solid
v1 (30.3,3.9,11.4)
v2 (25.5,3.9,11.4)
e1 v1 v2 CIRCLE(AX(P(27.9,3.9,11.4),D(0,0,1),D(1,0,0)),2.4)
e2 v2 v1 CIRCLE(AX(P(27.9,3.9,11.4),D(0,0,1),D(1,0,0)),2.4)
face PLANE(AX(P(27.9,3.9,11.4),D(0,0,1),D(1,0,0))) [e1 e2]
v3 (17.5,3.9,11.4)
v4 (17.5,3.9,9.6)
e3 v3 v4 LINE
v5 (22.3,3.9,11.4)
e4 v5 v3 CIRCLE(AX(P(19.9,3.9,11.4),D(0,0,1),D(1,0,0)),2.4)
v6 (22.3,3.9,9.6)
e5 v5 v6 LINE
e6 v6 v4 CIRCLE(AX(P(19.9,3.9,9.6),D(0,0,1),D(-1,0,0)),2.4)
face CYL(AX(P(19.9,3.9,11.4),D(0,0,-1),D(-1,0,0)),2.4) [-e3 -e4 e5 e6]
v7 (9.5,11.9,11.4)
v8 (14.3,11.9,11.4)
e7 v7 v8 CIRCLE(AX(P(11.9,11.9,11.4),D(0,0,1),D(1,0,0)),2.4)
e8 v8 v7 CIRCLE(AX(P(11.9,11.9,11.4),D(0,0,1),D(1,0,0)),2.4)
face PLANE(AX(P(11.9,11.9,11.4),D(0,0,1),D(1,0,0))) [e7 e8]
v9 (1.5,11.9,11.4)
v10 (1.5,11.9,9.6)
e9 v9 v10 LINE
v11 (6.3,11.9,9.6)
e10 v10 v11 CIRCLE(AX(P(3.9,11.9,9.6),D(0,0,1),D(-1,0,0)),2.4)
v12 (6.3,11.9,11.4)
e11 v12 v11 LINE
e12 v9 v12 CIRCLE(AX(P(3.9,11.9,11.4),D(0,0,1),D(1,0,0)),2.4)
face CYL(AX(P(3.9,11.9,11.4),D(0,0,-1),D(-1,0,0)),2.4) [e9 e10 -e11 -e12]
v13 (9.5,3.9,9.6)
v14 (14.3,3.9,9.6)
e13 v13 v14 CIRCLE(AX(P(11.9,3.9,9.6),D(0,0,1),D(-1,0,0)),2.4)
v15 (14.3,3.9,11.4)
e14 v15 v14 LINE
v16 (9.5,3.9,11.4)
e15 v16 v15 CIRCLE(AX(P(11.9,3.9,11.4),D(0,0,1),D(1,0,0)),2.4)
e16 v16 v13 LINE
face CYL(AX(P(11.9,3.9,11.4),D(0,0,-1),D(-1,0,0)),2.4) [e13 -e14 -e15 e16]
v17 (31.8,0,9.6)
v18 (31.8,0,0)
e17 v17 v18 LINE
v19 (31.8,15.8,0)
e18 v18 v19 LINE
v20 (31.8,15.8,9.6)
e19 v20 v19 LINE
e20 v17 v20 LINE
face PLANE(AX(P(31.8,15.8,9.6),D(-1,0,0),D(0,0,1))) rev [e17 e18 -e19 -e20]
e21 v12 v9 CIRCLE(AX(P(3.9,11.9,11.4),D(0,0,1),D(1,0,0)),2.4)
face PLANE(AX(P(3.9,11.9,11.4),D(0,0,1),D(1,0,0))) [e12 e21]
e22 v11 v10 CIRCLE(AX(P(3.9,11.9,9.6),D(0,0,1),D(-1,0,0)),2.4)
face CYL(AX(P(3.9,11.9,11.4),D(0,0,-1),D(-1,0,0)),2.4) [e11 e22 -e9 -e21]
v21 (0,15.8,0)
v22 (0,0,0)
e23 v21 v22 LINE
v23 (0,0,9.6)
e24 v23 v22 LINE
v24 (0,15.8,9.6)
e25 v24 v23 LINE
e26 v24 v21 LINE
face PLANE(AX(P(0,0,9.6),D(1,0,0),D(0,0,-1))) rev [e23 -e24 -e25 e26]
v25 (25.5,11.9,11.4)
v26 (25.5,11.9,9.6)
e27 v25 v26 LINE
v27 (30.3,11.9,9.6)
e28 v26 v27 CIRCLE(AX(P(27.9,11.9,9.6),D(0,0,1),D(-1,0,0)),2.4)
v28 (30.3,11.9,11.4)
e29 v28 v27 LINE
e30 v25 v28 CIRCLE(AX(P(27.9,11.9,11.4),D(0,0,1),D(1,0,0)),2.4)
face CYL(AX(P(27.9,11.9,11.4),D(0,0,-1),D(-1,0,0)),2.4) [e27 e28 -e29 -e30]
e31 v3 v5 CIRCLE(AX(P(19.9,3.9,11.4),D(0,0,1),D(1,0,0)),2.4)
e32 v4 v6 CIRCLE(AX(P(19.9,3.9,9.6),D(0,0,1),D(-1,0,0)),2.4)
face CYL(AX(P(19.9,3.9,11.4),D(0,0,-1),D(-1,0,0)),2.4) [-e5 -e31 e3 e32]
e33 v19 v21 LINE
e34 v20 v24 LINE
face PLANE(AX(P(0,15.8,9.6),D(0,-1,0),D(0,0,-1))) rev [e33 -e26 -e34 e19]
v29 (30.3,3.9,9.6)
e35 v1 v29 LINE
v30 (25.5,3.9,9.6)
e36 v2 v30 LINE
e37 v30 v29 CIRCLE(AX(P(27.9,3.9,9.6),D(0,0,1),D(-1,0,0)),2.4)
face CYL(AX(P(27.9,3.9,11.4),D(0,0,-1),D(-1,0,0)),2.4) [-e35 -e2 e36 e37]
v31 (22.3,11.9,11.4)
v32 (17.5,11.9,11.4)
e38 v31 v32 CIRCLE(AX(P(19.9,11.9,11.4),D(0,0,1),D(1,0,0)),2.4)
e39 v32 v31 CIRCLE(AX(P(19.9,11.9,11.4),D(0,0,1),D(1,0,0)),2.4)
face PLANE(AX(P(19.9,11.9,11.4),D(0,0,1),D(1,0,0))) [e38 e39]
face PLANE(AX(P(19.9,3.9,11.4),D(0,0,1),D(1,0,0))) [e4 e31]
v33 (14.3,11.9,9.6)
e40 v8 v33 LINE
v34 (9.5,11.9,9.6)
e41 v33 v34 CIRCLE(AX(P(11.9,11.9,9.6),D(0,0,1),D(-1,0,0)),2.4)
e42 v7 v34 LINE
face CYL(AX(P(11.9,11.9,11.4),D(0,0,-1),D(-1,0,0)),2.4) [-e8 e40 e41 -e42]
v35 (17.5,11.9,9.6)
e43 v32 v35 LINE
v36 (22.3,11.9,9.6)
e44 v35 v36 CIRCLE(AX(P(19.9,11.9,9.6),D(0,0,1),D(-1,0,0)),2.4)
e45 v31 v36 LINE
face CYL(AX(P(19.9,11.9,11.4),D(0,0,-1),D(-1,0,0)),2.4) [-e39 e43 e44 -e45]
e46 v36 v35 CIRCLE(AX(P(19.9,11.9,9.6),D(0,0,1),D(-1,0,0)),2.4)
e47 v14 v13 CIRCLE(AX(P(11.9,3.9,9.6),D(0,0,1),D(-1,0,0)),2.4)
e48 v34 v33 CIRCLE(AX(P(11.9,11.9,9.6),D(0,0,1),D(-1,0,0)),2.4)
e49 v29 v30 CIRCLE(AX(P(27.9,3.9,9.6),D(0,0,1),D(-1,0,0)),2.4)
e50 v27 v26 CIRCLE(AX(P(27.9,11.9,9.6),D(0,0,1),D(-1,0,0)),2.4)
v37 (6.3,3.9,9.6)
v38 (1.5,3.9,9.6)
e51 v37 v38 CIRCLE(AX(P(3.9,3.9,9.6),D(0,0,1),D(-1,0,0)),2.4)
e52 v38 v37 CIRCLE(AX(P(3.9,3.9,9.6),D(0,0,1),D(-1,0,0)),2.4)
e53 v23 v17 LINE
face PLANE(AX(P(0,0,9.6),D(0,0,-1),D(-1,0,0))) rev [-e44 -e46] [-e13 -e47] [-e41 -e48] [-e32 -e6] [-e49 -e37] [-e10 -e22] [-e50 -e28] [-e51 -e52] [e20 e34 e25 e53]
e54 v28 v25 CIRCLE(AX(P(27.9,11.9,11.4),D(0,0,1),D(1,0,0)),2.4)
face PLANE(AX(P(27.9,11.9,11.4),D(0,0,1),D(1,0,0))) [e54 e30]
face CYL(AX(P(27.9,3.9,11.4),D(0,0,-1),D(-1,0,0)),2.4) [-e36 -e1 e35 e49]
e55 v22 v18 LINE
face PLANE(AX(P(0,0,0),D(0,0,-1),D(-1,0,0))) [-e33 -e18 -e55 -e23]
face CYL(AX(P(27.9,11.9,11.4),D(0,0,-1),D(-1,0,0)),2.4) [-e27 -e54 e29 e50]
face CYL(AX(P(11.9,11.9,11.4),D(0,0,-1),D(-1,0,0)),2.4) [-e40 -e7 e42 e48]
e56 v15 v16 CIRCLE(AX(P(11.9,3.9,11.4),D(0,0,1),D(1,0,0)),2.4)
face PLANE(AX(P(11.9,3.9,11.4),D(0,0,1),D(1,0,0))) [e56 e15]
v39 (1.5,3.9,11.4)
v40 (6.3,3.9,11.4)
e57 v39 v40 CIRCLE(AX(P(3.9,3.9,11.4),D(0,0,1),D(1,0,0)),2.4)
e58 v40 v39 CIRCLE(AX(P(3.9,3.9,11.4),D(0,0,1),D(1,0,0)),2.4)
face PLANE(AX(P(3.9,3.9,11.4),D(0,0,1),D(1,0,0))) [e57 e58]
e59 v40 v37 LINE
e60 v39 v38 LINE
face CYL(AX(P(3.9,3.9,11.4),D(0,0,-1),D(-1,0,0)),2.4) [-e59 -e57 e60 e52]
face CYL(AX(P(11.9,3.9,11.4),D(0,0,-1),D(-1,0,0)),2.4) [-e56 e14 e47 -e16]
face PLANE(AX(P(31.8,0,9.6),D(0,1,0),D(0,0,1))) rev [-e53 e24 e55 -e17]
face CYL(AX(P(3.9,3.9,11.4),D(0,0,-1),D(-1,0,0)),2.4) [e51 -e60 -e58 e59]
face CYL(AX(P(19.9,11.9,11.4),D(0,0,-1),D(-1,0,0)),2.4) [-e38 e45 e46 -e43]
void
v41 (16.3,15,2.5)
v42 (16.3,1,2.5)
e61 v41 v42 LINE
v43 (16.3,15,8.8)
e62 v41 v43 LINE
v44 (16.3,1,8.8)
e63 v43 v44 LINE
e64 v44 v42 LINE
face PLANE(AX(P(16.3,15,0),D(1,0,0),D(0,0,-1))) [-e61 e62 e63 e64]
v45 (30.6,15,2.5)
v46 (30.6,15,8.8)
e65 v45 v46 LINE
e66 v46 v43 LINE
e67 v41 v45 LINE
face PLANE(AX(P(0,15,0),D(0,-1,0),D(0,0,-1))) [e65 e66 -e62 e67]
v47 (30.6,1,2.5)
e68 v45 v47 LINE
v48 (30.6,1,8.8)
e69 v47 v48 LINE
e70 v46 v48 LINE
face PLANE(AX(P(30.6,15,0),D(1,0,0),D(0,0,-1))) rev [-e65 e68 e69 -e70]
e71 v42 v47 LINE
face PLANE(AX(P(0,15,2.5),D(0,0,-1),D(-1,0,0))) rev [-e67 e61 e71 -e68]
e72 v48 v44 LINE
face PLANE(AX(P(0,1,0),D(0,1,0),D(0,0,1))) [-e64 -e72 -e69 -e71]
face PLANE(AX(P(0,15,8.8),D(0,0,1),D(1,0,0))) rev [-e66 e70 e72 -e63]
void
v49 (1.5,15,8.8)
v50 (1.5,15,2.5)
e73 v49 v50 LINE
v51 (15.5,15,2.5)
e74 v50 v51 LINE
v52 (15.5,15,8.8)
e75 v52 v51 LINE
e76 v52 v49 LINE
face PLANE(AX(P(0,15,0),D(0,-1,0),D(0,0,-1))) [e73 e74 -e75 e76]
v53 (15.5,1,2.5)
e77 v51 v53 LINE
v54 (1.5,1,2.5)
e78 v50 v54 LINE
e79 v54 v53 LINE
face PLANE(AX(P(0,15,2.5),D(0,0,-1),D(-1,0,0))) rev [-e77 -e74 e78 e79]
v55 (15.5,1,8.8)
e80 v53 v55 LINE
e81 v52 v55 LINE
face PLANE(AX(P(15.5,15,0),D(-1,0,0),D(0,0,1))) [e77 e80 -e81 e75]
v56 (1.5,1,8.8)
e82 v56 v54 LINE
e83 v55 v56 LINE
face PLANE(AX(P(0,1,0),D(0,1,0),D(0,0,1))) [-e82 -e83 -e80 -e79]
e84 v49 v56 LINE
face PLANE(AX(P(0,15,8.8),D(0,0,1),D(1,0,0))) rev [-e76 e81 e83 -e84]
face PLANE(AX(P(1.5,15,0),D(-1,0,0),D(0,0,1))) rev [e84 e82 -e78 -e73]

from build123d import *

# Parameters (mm, degrees)
BRICK_OUTLINE_SKETCH_W    = 31.8
BRICK_OUTLINE_SKETCH_H    = 15.8
BRICK_BODY_9_6_DEPTH      = 9.6
STUD_CIRCLES_SKETCH_R     = 2.4
STUDS_8X_4_8_DEPTH        = 1.8
UNDERSIDE_CUT_SKETCH_W    = 14
UNDERSIDE_CUT_SKETCH_H    = 6.3
UNDERSIDE_CUT_SKETCH_W_2  = 14.3
UNDERSIDE_CUT_DEPTH       = 15
UNDERSIDE_BOSS_SKETCH_W   = 14
UNDERSIDE_BOSS_SKETCH_H   = 6.3
UNDERSIDE_BOSS_SKETCH_W_2 = 14.3
UNDERSIDE_BOSS_1MM_DEPTH  = 1


with BuildPart() as part:
    # Brick Outline Sketch → Brick Body 9.6 (new body)
    with BuildSketch(Plane.XY):
        with Locations((15.9, 7.9)):
            Rectangle(BRICK_OUTLINE_SKETCH_W, BRICK_OUTLINE_SKETCH_H)
    extrude(amount=BRICK_BODY_9_6_DEPTH)

    # Stud Circles Sketch → Studs 8xØ4.8 (add)
    with BuildSketch(Plane.XY.offset(9.6)):
        with Locations(Location((3.9, 11.9, 0), (0, 0, 180))):
            Circle(STUD_CIRCLES_SKETCH_R)
        with Locations(Location((3.9, 3.9, 0), (0, 0, 180))):
            Circle(STUD_CIRCLES_SKETCH_R)
        with Locations(Location((11.9, 11.9, 0), (0, 0, 180))):
            Circle(STUD_CIRCLES_SKETCH_R)
        with Locations(Location((19.9, 11.9, 0), (0, 0, 180))):
            Circle(STUD_CIRCLES_SKETCH_R)
        with Locations(Location((27.9, 11.9, 0), (0, 0, 180))):
            Circle(STUD_CIRCLES_SKETCH_R)
        with Locations(Location((11.9, 3.9, 0), (0, 0, 180))):
            Circle(STUD_CIRCLES_SKETCH_R)
        with Locations(Location((19.9, 3.9, 0), (0, 0, 180))):
            Circle(STUD_CIRCLES_SKETCH_R)
        with Locations(Location((27.9, 3.9, 0), (0, 0, 180))):
            Circle(STUD_CIRCLES_SKETCH_R)
    extrude(amount=STUDS_8X_4_8_DEPTH)

    # Underside Cut Sketch → Underside Cut (cut)
    with BuildSketch(Plane.XZ):
        with Locations((8.5, 5.65)):
            Rectangle(UNDERSIDE_CUT_SKETCH_W, UNDERSIDE_CUT_SKETCH_H)
        with Locations((23.45, 5.65)):
            Rectangle(UNDERSIDE_CUT_SKETCH_W_2, UNDERSIDE_CUT_SKETCH_H)
    extrude(amount=-UNDERSIDE_CUT_DEPTH, mode=Mode.SUBTRACT)

    # Underside Boss Sketch → Underside Boss 1mm (add)
    with BuildSketch(Plane.XZ):
        with Locations((8.5, 5.65)):
            Rectangle(UNDERSIDE_BOSS_SKETCH_W, UNDERSIDE_BOSS_SKETCH_H)
        with Locations((23.45, 5.65)):
            Rectangle(UNDERSIDE_BOSS_SKETCH_W_2, UNDERSIDE_BOSS_SKETCH_H)
    extrude(amount=-UNDERSIDE_BOSS_1MM_DEPTH)


solid = part.part
